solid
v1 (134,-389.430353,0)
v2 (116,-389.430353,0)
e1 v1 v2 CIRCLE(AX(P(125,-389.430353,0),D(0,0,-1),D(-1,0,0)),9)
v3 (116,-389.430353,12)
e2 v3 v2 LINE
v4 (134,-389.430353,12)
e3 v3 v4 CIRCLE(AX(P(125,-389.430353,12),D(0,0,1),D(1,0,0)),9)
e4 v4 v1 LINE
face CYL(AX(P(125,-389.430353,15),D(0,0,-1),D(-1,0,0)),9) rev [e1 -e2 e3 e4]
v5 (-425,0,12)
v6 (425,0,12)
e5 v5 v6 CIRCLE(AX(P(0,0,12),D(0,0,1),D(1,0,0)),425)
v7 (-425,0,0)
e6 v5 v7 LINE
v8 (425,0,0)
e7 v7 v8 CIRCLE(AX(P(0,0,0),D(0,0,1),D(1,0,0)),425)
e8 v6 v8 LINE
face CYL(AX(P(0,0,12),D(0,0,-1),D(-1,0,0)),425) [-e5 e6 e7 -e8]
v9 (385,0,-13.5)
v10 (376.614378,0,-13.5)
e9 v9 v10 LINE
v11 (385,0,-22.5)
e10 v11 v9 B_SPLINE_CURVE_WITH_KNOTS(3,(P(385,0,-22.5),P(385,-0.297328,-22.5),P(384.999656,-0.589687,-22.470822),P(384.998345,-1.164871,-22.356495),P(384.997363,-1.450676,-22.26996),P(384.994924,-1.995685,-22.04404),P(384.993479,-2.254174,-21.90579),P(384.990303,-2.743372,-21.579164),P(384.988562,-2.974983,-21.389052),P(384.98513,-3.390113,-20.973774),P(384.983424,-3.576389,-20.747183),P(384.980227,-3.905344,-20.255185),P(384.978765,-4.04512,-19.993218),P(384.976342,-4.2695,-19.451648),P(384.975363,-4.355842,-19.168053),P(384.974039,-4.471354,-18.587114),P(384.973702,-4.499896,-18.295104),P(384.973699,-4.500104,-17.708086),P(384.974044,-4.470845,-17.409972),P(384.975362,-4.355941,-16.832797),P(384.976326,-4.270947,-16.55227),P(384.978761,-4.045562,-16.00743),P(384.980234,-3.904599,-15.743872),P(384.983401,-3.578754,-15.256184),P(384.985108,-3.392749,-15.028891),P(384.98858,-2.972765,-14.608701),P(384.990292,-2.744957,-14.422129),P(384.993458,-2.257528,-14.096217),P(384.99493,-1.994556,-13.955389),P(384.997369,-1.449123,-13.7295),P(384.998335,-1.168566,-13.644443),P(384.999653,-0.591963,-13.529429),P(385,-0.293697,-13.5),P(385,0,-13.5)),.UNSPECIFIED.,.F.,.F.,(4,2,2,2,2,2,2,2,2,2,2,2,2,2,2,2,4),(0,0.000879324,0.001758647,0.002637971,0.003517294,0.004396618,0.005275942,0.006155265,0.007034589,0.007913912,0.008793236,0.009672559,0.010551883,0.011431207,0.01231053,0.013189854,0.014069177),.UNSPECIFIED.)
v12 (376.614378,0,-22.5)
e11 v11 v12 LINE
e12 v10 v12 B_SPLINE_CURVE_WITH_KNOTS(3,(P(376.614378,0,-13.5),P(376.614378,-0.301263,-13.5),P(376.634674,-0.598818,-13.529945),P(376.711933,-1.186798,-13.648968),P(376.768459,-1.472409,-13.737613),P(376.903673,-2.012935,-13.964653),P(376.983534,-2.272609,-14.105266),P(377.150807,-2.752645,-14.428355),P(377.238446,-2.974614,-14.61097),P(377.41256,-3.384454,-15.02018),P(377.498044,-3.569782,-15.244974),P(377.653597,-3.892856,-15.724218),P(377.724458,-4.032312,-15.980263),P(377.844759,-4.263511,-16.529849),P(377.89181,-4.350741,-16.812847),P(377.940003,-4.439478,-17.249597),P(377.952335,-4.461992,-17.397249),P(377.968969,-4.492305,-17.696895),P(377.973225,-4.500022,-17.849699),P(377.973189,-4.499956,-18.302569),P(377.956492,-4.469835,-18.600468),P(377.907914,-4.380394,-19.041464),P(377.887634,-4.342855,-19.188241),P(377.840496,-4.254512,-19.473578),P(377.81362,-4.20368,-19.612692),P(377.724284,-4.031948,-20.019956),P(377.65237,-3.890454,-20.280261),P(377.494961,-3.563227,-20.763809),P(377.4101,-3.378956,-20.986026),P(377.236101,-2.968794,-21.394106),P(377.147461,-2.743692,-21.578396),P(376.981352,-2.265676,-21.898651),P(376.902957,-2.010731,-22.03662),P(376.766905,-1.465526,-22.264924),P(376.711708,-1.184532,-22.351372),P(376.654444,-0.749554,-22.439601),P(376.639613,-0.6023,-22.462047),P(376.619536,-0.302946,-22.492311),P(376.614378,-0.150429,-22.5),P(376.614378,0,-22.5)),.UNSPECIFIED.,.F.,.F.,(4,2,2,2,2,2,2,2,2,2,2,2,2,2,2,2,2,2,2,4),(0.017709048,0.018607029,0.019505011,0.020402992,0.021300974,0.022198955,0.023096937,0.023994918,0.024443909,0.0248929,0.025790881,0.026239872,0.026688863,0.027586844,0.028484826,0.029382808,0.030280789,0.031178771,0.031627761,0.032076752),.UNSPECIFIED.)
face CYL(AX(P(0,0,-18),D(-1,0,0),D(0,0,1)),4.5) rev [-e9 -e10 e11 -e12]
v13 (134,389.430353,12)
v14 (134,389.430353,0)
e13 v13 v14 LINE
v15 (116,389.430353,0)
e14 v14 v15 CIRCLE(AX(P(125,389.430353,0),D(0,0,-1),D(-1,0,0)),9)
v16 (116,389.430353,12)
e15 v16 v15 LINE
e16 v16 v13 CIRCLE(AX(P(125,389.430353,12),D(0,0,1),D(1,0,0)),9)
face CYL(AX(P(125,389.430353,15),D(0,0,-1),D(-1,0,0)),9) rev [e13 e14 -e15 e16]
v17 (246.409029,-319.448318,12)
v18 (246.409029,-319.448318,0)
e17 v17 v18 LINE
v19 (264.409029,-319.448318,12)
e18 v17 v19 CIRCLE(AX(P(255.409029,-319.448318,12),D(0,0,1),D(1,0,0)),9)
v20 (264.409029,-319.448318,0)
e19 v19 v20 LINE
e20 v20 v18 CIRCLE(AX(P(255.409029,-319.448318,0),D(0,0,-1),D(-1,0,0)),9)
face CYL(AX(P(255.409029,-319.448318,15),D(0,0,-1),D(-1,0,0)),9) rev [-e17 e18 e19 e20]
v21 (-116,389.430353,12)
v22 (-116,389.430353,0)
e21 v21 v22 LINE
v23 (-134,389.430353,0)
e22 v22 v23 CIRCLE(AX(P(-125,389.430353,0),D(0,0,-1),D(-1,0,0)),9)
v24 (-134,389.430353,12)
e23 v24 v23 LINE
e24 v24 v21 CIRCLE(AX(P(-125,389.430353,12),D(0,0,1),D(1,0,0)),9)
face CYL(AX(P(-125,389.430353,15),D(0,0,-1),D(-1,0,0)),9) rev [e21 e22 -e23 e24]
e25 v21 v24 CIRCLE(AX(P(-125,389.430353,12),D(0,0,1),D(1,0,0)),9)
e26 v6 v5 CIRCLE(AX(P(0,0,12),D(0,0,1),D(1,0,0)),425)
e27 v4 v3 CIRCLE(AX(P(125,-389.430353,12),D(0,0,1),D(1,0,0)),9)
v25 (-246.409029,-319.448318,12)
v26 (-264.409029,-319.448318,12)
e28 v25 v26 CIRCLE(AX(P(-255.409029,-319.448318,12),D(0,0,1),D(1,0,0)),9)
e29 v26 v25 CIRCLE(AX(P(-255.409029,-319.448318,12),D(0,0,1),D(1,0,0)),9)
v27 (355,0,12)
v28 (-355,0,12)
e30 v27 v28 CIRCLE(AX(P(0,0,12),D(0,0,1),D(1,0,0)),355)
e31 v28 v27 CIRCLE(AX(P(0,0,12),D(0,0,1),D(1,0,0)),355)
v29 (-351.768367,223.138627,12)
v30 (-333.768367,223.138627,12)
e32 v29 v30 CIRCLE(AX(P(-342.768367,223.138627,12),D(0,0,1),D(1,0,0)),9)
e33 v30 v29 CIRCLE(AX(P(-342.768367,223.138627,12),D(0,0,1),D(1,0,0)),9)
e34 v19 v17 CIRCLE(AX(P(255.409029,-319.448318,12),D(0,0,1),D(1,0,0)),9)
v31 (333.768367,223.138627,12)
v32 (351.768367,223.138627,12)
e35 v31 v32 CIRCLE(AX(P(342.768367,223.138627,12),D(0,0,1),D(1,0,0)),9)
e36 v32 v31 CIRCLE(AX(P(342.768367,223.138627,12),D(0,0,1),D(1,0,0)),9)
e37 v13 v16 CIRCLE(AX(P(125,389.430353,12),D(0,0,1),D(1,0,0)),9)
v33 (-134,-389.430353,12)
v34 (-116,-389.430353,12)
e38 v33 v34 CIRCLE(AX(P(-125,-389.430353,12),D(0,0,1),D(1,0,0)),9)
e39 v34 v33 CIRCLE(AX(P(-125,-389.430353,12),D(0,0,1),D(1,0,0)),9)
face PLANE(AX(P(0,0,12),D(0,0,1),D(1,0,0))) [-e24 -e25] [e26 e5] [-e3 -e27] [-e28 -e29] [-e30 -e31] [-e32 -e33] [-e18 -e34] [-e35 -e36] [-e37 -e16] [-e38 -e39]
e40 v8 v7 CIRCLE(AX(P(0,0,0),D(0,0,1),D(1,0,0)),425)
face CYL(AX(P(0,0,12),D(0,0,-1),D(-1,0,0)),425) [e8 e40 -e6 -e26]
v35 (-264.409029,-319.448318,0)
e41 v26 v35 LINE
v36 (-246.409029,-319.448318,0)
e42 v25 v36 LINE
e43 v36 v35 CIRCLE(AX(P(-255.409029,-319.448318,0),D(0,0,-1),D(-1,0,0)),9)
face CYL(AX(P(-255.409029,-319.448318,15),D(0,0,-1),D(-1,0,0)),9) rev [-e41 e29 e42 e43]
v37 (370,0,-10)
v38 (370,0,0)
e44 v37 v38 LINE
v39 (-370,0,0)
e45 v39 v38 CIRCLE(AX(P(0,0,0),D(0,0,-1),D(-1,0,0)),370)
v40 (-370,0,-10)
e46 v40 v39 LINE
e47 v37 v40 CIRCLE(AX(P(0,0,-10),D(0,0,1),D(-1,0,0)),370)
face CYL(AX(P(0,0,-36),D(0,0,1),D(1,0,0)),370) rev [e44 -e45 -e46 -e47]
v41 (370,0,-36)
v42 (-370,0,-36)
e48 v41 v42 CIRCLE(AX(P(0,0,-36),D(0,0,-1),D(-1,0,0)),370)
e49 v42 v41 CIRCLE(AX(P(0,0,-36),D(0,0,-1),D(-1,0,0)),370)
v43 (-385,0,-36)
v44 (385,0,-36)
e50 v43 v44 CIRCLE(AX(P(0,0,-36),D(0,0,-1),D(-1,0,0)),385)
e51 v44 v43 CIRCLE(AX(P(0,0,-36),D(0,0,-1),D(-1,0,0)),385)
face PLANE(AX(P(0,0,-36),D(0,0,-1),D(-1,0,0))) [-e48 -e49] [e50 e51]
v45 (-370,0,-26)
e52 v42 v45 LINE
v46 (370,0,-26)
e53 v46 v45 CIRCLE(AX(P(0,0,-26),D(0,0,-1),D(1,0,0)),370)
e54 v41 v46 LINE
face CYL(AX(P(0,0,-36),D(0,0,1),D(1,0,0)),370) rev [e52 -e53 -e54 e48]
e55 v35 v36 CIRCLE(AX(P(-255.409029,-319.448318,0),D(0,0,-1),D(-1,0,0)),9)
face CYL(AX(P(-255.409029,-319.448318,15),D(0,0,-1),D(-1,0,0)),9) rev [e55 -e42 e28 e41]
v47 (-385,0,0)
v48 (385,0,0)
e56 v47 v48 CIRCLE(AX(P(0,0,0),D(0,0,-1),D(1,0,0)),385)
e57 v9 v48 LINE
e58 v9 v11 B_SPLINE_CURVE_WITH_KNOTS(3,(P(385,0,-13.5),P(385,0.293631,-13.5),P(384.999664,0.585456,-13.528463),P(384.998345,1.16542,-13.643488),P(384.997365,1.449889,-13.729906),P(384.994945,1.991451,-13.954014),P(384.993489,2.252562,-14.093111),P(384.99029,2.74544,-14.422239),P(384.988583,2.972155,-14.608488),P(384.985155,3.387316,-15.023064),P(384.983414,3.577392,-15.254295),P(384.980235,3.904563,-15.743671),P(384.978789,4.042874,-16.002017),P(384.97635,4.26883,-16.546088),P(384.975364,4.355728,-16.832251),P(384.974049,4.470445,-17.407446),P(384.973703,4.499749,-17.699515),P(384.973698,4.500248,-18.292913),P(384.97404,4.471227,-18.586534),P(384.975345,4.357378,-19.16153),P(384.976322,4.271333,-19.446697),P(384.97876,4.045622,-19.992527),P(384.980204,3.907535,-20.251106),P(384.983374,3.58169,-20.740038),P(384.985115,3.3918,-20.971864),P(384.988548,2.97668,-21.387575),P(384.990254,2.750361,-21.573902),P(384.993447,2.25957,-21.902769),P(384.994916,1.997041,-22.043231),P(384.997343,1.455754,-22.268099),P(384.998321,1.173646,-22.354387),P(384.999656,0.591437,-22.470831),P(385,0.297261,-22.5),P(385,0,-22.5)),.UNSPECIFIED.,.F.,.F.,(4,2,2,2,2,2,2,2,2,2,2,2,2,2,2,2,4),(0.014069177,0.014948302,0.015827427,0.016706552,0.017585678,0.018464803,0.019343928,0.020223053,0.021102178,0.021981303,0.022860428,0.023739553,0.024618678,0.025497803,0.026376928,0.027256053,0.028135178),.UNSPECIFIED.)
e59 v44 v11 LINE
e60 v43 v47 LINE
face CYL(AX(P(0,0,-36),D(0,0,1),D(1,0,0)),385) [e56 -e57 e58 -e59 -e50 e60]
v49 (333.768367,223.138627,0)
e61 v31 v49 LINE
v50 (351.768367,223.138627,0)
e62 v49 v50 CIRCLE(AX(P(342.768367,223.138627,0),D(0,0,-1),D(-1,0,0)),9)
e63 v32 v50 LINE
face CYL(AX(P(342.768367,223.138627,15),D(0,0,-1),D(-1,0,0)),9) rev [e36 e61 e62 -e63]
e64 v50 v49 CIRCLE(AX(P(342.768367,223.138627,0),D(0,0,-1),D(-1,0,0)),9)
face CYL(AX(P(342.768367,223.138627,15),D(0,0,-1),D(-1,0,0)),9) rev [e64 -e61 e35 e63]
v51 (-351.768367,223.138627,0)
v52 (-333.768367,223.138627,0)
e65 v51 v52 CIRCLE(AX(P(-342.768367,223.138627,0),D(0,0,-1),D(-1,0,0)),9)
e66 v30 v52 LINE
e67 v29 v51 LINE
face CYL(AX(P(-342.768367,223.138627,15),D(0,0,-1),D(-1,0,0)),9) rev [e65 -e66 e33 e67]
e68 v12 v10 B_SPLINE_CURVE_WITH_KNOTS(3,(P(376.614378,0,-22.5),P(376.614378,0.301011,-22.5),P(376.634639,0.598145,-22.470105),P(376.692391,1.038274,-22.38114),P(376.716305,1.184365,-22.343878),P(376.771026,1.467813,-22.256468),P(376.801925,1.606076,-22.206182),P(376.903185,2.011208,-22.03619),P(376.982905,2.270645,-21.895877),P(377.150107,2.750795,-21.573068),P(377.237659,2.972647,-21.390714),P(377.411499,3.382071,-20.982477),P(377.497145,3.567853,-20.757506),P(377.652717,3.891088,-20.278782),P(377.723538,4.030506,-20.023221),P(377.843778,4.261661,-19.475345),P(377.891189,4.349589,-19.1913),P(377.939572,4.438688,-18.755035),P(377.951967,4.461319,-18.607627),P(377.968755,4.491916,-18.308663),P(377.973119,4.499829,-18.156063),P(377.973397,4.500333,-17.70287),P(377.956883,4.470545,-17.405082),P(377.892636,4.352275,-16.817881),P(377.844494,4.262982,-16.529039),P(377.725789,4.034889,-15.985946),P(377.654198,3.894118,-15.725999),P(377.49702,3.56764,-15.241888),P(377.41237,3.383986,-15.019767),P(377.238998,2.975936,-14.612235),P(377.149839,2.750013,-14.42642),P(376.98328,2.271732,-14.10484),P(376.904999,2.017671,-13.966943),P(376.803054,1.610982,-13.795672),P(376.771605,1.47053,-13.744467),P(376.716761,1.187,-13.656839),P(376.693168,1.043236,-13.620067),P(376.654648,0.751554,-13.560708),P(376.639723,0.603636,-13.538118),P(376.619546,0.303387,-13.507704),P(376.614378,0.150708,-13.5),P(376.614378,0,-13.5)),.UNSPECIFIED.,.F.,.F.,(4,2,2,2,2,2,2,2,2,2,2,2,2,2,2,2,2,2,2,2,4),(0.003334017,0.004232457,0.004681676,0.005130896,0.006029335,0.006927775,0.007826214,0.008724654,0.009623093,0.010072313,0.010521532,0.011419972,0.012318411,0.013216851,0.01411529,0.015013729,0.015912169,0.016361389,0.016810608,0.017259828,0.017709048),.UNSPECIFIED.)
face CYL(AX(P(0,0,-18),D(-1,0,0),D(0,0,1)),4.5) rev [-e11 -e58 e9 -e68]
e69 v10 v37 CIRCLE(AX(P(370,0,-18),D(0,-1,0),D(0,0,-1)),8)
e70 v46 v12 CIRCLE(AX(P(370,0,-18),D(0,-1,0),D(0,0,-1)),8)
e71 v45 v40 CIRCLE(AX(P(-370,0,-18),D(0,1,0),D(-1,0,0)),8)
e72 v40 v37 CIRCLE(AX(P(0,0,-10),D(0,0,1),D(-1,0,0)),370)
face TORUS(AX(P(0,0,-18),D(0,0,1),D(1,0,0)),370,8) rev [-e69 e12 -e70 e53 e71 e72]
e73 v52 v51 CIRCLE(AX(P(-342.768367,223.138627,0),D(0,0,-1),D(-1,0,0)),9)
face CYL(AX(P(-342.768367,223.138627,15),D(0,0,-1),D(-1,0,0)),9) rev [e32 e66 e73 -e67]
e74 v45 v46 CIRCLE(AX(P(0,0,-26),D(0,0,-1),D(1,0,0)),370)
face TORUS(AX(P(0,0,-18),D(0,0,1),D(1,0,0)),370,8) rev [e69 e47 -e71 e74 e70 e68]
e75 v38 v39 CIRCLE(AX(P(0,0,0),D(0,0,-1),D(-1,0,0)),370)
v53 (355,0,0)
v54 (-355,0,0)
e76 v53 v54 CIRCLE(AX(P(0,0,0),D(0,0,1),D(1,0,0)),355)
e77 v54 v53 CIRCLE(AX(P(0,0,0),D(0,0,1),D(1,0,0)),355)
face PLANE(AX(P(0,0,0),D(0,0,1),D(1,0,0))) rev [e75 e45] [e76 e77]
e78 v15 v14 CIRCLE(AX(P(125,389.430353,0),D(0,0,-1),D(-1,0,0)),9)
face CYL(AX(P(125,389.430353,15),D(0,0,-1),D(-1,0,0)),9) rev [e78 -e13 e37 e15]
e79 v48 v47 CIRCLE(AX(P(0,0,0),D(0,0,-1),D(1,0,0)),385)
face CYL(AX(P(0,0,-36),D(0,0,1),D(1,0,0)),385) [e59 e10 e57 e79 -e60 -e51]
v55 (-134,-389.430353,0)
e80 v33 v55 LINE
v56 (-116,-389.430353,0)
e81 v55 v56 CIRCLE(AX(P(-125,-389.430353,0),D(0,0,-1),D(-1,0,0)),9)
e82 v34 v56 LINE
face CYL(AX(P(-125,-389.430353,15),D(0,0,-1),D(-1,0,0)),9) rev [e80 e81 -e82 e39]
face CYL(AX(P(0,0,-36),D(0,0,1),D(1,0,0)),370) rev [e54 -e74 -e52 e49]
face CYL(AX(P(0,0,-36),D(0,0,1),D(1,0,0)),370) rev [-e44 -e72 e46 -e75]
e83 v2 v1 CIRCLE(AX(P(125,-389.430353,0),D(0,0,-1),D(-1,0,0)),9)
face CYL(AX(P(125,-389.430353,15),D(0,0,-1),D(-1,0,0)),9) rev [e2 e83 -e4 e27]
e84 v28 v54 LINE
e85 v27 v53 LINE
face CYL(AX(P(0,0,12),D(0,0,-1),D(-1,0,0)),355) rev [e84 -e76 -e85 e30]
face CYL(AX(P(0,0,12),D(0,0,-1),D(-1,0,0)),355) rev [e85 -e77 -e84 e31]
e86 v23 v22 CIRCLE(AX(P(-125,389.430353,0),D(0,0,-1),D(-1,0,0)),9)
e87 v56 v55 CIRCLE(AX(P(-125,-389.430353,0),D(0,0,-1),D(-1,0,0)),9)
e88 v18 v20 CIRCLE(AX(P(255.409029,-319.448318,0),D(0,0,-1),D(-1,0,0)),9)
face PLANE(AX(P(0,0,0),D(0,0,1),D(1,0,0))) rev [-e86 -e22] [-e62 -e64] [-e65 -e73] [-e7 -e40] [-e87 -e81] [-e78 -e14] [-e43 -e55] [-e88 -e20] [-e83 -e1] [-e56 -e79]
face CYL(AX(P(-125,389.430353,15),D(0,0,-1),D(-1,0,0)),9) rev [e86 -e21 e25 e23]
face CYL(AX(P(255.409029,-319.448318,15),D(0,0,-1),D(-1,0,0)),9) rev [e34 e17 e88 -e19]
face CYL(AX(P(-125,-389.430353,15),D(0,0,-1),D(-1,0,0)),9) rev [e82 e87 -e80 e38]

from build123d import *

# Parameters (mm, degrees)
SKETCH_1_R          = 425
SKETCH_1_R_2        = 355
EXTRUDE_2_DEPTH     = 12
SKETCH_3_R          = 385
SKETCH_3_R_2        = 370
EXTRUDE_3_DEPTH     = 36
SWEEP_2_PROFILE_R   = 8
SKETCH_23_W         = 4.5
SKETCH_23_H         = 385
SKETCH_24_R         = 9
CUT_EXTRUDE_1_DEPTH = 15


with BuildPart() as part:
    # 草图1 → 凸台-拉伸2 (new body)
    with BuildSketch(Plane.XY):
        Circle(SKETCH_1_R)
        Circle(SKETCH_1_R_2, mode=Mode.SUBTRACT)
    extrude(amount=EXTRUDE_2_DEPTH)

    # 草图3 → 凸台-拉伸3 (add)
    with BuildSketch(Plane(origin=(0, 0, 0), x_dir=(-1, 0, 0), z_dir=(0, 0, -1))):
        with Locations(Location((0, 0, 0), (0, 0, 180))):
            Circle(SKETCH_3_R)
        Circle(SKETCH_3_R_2, mode=Mode.SUBTRACT)
    extrude(amount=EXTRUDE_3_DEPTH)

    # 切除-扫描2: sweep along a path in 草图4
    with BuildLine(Plane.XY.offset(-18)) as sweep_2_path:
        CenterArc((0, 0), 370, 0, 360)
    # 切除-扫描2 profile (on start of the path) → 切除-扫描2 (sweep, cut)
    with BuildSketch(Plane(origin=(370, 0, -18), x_dir=(0, 0, 1), z_dir=(0, 1, 0))):
        Circle(SWEEP_2_PROFILE_R)
    sweep(path=sweep_2_path.line, mode=Mode.SUBTRACT)

    # 草图23 → M10x1.0 螺纹孔1 (revolve, cut)
    with BuildSketch(Plane(origin=(0, 0, -18), x_dir=(0, 0, 1), z_dir=(0, 1, 0))):
        with Locations((2.25, 192.5)):
            Rectangle(SKETCH_23_W, SKETCH_23_H)
    revolve(axis=Axis((-6.35, 0, -18), (1, 0, 0)), mode=Mode.SUBTRACT)

    # 草图24 → 切除-拉伸1 (cut)
    with BuildSketch(Plane(origin=(0, 0, 0), x_dir=(-1, 0, 0), z_dir=(0, 0, -1))):
        with Locations((-125, -389.430353208)):
            Circle(SKETCH_24_R)
        with Locations((125, -389.430353208)):
            Circle(SKETCH_24_R)
        with Locations((-255.40902876, -319.448318243)):
            Circle(SKETCH_24_R)
        with Locations((255.40902876, -319.448318243)):
            Circle(SKETCH_24_R)
        with Locations((-125, 389.430353208)):
            Circle(SKETCH_24_R)
        with Locations((125, 389.430353208)):
            Circle(SKETCH_24_R)
        with Locations((342.768366919, 223.138626507)):
            Circle(SKETCH_24_R)
        with Locations((-342.768366919, 223.138626507)):
            Circle(SKETCH_24_R)
    extrude(amount=-CUT_EXTRUDE_1_DEPTH, mode=Mode.SUBTRACT)


solid = part.part
